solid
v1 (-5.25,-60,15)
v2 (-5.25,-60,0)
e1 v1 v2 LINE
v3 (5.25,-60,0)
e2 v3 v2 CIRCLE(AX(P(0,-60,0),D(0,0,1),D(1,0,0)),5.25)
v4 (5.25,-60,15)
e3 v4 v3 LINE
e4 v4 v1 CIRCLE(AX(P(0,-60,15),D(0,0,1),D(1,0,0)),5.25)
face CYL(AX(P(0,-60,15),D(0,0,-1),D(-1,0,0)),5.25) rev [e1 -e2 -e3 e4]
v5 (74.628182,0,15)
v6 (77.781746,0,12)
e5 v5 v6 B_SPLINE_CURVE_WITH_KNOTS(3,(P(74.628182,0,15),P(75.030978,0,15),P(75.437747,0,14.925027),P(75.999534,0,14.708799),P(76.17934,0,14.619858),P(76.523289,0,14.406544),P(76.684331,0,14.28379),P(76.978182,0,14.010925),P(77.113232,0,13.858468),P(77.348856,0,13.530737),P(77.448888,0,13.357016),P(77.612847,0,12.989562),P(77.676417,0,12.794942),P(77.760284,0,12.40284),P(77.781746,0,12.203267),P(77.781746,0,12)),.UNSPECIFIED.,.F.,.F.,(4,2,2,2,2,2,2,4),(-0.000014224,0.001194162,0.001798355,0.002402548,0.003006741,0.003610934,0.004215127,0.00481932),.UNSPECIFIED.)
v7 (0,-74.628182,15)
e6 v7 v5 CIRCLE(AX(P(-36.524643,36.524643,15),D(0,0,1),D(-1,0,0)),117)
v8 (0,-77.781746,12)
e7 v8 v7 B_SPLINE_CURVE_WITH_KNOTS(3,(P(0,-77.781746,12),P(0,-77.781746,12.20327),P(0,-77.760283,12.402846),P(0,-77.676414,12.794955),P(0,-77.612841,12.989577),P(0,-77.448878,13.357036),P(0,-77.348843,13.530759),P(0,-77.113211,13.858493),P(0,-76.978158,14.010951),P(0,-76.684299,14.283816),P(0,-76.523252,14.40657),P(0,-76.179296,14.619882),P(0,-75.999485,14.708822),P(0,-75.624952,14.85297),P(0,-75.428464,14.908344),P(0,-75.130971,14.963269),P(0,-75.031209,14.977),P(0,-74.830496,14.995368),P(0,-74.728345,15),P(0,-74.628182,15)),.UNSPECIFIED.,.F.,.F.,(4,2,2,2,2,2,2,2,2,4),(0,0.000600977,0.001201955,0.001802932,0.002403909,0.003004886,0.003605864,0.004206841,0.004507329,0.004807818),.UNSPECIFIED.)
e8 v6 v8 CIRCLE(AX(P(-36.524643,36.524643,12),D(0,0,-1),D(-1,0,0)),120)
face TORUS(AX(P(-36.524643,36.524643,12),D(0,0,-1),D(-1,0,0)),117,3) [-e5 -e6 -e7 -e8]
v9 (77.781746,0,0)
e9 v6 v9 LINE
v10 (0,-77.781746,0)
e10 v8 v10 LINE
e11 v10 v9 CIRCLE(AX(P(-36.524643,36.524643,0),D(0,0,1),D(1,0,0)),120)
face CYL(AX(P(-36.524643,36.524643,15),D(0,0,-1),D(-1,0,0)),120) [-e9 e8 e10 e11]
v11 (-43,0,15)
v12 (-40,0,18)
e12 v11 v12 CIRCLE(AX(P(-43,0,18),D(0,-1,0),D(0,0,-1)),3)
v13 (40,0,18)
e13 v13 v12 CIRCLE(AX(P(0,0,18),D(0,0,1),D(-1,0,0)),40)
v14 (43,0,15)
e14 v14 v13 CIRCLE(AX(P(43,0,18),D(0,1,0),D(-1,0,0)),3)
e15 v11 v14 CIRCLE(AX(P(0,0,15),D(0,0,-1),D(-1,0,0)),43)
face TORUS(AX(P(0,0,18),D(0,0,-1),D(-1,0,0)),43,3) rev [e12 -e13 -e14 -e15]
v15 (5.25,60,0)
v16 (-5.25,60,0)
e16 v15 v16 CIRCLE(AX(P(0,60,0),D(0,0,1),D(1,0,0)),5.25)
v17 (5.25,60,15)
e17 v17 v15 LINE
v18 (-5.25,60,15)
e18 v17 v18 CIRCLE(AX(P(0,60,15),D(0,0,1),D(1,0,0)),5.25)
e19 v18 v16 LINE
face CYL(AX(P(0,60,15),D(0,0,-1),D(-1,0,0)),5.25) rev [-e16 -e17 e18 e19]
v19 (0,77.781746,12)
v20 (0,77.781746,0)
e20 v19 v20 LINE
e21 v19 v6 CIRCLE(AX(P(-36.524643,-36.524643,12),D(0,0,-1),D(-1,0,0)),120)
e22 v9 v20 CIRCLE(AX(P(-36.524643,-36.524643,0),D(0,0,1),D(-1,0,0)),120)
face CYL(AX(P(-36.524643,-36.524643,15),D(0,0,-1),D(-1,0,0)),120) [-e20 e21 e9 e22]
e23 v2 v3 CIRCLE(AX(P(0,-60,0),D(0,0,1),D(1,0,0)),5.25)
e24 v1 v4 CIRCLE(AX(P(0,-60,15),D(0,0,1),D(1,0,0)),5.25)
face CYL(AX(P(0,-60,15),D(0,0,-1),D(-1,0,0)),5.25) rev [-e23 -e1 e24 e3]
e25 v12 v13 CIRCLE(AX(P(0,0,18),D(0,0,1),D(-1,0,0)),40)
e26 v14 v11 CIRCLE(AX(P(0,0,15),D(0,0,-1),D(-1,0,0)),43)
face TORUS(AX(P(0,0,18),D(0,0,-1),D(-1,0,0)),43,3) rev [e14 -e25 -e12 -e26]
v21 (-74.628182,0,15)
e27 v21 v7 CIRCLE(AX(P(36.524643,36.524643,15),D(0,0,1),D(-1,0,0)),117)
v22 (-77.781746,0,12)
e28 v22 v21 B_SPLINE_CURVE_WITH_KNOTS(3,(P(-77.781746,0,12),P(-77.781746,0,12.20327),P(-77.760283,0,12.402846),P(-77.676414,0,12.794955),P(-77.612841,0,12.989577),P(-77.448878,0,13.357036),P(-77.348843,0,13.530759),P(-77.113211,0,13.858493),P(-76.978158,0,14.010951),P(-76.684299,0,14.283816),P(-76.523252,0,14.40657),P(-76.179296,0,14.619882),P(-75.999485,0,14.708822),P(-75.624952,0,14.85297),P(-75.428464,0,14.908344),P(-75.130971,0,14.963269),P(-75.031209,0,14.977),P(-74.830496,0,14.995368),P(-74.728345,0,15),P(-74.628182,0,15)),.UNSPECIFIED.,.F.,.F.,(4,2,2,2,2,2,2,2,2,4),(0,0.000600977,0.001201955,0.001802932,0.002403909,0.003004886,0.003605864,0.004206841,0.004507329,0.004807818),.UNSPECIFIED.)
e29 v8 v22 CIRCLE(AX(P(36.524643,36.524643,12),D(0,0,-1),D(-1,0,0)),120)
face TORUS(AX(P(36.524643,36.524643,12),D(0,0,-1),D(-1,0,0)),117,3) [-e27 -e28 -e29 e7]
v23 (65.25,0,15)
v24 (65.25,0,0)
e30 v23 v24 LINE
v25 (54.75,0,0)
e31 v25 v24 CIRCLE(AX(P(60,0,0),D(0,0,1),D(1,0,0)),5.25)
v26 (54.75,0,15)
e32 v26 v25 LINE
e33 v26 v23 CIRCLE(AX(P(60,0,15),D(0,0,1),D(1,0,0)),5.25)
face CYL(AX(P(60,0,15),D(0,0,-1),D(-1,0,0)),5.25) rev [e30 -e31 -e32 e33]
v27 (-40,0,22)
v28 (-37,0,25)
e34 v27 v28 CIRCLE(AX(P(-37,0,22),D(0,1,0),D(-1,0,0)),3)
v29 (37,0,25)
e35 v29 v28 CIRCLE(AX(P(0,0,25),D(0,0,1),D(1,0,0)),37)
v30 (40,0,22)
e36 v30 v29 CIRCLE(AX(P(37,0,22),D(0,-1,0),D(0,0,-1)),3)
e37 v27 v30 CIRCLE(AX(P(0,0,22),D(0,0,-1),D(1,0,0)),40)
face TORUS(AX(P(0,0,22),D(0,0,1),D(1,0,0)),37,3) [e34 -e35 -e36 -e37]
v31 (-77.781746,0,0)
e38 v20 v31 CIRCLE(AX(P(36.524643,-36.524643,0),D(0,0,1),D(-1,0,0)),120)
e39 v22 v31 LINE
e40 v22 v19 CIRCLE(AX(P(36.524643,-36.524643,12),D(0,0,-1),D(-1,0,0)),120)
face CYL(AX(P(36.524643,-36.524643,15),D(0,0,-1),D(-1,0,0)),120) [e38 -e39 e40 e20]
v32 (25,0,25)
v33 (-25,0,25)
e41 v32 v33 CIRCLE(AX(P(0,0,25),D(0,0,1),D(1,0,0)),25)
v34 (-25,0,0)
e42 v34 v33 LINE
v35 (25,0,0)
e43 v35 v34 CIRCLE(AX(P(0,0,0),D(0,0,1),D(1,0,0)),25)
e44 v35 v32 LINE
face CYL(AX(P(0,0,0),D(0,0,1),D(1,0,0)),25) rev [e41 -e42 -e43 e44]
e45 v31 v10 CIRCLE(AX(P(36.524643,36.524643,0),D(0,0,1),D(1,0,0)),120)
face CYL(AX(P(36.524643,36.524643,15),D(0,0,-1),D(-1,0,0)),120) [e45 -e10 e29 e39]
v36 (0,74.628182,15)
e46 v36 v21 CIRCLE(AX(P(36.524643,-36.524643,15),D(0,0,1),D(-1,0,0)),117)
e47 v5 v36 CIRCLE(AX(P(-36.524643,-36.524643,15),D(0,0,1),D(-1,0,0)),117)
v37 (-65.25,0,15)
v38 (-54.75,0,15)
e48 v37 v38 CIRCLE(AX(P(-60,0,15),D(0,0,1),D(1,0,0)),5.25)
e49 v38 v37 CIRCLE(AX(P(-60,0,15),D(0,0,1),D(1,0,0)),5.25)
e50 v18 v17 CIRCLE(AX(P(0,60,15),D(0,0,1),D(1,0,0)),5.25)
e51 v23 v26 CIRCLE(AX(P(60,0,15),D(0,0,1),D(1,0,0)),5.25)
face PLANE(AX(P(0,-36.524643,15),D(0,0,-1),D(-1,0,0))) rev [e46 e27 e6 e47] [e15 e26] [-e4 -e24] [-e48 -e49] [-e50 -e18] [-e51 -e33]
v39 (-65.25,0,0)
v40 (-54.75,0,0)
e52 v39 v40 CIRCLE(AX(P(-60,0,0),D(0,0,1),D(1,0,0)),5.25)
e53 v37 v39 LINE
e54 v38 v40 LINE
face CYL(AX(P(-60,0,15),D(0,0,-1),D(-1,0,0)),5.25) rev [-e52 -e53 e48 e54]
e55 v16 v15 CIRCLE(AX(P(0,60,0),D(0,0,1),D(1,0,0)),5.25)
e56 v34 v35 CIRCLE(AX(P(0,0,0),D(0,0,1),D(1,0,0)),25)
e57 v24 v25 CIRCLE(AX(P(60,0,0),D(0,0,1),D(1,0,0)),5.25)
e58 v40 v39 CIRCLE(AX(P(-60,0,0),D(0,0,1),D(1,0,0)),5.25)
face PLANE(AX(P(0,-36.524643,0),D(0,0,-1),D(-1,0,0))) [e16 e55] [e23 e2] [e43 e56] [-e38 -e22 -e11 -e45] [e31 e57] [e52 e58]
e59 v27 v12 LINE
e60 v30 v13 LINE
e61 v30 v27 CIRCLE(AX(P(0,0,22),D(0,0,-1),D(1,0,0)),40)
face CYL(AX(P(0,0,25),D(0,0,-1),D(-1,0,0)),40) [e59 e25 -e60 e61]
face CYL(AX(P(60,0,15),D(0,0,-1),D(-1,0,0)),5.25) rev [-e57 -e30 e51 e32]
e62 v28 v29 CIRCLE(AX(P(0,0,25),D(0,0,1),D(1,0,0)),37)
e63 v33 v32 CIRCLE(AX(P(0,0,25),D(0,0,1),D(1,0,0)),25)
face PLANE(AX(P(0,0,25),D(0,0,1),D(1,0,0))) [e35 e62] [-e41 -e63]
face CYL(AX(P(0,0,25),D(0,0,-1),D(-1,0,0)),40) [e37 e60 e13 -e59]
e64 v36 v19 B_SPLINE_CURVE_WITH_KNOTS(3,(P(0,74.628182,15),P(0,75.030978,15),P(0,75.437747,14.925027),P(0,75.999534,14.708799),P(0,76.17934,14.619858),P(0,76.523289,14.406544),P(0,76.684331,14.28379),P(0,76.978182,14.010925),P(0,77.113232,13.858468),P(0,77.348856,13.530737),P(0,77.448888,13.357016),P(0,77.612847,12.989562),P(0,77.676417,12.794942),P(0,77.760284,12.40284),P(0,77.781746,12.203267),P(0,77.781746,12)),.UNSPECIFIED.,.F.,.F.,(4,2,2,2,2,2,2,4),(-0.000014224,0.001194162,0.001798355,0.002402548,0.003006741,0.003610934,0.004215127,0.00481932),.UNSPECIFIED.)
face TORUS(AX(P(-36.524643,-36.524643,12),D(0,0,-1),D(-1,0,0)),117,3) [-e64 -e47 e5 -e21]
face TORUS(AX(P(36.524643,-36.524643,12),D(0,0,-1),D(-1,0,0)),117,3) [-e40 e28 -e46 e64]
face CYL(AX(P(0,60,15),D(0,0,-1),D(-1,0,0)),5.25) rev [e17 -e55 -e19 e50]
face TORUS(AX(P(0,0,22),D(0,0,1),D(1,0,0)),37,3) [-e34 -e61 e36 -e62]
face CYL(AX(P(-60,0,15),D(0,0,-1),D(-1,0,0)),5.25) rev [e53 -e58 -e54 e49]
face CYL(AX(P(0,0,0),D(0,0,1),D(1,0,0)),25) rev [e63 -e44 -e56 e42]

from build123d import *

# Parameters (mm, degrees)
SKETCH_1_R          = 5.25
EXTRUDE_1_DEPTH     = 15
SKETCH_2_R          = 40
EXTRUDE_2_DEPTH     = 10
SKETCH_3_R          = 25
CUT_EXTRUDE_1_DEPTH = 113.805141727
FILLET_1_R          = 3


with BuildPart() as part:
    # 草图1 → 凸台-拉伸1 (new body)
    with BuildSketch(Plane.XY):
        with BuildLine():
            ThreePointArc((0, 77.781745931), (48.328171063, 48.328171063), (77.781745931, 0))
            ThreePointArc((77.781745931, 0), (48.328171063, -48.328171063), (0, -77.781745931))
            ThreePointArc((0, -77.781745931), (-48.328171063, -48.328171063), (-77.781745931, 0))
            ThreePointArc((-77.781745931, 0), (-48.328171063, 48.328171063), (0, 77.781745931))
        make_face()
        with Locations((0, 60)):
            Circle(SKETCH_1_R, mode=Mode.SUBTRACT)
        with Locations((60, 0)):
            Circle(SKETCH_1_R, mode=Mode.SUBTRACT)
        with Locations((0, -60)):
            Circle(SKETCH_1_R, mode=Mode.SUBTRACT)
        with Locations((-60, 0)):
            Circle(SKETCH_1_R, mode=Mode.SUBTRACT)
    extrude(amount=EXTRUDE_1_DEPTH)

    # 草图2 → 凸台-拉伸2 (add)
    with BuildSketch(Plane.XY.offset(15)):
        with Locations(Location((0, 0, 0), (0, 0, 180))):
            Circle(SKETCH_2_R)
    extrude(amount=EXTRUDE_2_DEPTH)

    # 草图3 → 切除-拉伸1 (cut, through all)
    with BuildSketch(Plane.XY.offset(25)):
        Circle(SKETCH_3_R)
    extrude(amount=-CUT_EXTRUDE_1_DEPTH, mode=Mode.SUBTRACT)

    # 圆角1
    fillet_1_edges = [part.edges().sort_by_distance(p)[0] for p in [
        (48.328171063, -48.328171063, 15),
        (48.328171063, 48.328171063, 15),
        (40, 0, 15),
        (40, 0, 25),
        (-48.328171063, 48.328171063, 15),
        (-48.328171063, -48.328171063, 15),
    ]]
    fillet(fillet_1_edges, radius=FILLET_1_R)


solid = part.part
